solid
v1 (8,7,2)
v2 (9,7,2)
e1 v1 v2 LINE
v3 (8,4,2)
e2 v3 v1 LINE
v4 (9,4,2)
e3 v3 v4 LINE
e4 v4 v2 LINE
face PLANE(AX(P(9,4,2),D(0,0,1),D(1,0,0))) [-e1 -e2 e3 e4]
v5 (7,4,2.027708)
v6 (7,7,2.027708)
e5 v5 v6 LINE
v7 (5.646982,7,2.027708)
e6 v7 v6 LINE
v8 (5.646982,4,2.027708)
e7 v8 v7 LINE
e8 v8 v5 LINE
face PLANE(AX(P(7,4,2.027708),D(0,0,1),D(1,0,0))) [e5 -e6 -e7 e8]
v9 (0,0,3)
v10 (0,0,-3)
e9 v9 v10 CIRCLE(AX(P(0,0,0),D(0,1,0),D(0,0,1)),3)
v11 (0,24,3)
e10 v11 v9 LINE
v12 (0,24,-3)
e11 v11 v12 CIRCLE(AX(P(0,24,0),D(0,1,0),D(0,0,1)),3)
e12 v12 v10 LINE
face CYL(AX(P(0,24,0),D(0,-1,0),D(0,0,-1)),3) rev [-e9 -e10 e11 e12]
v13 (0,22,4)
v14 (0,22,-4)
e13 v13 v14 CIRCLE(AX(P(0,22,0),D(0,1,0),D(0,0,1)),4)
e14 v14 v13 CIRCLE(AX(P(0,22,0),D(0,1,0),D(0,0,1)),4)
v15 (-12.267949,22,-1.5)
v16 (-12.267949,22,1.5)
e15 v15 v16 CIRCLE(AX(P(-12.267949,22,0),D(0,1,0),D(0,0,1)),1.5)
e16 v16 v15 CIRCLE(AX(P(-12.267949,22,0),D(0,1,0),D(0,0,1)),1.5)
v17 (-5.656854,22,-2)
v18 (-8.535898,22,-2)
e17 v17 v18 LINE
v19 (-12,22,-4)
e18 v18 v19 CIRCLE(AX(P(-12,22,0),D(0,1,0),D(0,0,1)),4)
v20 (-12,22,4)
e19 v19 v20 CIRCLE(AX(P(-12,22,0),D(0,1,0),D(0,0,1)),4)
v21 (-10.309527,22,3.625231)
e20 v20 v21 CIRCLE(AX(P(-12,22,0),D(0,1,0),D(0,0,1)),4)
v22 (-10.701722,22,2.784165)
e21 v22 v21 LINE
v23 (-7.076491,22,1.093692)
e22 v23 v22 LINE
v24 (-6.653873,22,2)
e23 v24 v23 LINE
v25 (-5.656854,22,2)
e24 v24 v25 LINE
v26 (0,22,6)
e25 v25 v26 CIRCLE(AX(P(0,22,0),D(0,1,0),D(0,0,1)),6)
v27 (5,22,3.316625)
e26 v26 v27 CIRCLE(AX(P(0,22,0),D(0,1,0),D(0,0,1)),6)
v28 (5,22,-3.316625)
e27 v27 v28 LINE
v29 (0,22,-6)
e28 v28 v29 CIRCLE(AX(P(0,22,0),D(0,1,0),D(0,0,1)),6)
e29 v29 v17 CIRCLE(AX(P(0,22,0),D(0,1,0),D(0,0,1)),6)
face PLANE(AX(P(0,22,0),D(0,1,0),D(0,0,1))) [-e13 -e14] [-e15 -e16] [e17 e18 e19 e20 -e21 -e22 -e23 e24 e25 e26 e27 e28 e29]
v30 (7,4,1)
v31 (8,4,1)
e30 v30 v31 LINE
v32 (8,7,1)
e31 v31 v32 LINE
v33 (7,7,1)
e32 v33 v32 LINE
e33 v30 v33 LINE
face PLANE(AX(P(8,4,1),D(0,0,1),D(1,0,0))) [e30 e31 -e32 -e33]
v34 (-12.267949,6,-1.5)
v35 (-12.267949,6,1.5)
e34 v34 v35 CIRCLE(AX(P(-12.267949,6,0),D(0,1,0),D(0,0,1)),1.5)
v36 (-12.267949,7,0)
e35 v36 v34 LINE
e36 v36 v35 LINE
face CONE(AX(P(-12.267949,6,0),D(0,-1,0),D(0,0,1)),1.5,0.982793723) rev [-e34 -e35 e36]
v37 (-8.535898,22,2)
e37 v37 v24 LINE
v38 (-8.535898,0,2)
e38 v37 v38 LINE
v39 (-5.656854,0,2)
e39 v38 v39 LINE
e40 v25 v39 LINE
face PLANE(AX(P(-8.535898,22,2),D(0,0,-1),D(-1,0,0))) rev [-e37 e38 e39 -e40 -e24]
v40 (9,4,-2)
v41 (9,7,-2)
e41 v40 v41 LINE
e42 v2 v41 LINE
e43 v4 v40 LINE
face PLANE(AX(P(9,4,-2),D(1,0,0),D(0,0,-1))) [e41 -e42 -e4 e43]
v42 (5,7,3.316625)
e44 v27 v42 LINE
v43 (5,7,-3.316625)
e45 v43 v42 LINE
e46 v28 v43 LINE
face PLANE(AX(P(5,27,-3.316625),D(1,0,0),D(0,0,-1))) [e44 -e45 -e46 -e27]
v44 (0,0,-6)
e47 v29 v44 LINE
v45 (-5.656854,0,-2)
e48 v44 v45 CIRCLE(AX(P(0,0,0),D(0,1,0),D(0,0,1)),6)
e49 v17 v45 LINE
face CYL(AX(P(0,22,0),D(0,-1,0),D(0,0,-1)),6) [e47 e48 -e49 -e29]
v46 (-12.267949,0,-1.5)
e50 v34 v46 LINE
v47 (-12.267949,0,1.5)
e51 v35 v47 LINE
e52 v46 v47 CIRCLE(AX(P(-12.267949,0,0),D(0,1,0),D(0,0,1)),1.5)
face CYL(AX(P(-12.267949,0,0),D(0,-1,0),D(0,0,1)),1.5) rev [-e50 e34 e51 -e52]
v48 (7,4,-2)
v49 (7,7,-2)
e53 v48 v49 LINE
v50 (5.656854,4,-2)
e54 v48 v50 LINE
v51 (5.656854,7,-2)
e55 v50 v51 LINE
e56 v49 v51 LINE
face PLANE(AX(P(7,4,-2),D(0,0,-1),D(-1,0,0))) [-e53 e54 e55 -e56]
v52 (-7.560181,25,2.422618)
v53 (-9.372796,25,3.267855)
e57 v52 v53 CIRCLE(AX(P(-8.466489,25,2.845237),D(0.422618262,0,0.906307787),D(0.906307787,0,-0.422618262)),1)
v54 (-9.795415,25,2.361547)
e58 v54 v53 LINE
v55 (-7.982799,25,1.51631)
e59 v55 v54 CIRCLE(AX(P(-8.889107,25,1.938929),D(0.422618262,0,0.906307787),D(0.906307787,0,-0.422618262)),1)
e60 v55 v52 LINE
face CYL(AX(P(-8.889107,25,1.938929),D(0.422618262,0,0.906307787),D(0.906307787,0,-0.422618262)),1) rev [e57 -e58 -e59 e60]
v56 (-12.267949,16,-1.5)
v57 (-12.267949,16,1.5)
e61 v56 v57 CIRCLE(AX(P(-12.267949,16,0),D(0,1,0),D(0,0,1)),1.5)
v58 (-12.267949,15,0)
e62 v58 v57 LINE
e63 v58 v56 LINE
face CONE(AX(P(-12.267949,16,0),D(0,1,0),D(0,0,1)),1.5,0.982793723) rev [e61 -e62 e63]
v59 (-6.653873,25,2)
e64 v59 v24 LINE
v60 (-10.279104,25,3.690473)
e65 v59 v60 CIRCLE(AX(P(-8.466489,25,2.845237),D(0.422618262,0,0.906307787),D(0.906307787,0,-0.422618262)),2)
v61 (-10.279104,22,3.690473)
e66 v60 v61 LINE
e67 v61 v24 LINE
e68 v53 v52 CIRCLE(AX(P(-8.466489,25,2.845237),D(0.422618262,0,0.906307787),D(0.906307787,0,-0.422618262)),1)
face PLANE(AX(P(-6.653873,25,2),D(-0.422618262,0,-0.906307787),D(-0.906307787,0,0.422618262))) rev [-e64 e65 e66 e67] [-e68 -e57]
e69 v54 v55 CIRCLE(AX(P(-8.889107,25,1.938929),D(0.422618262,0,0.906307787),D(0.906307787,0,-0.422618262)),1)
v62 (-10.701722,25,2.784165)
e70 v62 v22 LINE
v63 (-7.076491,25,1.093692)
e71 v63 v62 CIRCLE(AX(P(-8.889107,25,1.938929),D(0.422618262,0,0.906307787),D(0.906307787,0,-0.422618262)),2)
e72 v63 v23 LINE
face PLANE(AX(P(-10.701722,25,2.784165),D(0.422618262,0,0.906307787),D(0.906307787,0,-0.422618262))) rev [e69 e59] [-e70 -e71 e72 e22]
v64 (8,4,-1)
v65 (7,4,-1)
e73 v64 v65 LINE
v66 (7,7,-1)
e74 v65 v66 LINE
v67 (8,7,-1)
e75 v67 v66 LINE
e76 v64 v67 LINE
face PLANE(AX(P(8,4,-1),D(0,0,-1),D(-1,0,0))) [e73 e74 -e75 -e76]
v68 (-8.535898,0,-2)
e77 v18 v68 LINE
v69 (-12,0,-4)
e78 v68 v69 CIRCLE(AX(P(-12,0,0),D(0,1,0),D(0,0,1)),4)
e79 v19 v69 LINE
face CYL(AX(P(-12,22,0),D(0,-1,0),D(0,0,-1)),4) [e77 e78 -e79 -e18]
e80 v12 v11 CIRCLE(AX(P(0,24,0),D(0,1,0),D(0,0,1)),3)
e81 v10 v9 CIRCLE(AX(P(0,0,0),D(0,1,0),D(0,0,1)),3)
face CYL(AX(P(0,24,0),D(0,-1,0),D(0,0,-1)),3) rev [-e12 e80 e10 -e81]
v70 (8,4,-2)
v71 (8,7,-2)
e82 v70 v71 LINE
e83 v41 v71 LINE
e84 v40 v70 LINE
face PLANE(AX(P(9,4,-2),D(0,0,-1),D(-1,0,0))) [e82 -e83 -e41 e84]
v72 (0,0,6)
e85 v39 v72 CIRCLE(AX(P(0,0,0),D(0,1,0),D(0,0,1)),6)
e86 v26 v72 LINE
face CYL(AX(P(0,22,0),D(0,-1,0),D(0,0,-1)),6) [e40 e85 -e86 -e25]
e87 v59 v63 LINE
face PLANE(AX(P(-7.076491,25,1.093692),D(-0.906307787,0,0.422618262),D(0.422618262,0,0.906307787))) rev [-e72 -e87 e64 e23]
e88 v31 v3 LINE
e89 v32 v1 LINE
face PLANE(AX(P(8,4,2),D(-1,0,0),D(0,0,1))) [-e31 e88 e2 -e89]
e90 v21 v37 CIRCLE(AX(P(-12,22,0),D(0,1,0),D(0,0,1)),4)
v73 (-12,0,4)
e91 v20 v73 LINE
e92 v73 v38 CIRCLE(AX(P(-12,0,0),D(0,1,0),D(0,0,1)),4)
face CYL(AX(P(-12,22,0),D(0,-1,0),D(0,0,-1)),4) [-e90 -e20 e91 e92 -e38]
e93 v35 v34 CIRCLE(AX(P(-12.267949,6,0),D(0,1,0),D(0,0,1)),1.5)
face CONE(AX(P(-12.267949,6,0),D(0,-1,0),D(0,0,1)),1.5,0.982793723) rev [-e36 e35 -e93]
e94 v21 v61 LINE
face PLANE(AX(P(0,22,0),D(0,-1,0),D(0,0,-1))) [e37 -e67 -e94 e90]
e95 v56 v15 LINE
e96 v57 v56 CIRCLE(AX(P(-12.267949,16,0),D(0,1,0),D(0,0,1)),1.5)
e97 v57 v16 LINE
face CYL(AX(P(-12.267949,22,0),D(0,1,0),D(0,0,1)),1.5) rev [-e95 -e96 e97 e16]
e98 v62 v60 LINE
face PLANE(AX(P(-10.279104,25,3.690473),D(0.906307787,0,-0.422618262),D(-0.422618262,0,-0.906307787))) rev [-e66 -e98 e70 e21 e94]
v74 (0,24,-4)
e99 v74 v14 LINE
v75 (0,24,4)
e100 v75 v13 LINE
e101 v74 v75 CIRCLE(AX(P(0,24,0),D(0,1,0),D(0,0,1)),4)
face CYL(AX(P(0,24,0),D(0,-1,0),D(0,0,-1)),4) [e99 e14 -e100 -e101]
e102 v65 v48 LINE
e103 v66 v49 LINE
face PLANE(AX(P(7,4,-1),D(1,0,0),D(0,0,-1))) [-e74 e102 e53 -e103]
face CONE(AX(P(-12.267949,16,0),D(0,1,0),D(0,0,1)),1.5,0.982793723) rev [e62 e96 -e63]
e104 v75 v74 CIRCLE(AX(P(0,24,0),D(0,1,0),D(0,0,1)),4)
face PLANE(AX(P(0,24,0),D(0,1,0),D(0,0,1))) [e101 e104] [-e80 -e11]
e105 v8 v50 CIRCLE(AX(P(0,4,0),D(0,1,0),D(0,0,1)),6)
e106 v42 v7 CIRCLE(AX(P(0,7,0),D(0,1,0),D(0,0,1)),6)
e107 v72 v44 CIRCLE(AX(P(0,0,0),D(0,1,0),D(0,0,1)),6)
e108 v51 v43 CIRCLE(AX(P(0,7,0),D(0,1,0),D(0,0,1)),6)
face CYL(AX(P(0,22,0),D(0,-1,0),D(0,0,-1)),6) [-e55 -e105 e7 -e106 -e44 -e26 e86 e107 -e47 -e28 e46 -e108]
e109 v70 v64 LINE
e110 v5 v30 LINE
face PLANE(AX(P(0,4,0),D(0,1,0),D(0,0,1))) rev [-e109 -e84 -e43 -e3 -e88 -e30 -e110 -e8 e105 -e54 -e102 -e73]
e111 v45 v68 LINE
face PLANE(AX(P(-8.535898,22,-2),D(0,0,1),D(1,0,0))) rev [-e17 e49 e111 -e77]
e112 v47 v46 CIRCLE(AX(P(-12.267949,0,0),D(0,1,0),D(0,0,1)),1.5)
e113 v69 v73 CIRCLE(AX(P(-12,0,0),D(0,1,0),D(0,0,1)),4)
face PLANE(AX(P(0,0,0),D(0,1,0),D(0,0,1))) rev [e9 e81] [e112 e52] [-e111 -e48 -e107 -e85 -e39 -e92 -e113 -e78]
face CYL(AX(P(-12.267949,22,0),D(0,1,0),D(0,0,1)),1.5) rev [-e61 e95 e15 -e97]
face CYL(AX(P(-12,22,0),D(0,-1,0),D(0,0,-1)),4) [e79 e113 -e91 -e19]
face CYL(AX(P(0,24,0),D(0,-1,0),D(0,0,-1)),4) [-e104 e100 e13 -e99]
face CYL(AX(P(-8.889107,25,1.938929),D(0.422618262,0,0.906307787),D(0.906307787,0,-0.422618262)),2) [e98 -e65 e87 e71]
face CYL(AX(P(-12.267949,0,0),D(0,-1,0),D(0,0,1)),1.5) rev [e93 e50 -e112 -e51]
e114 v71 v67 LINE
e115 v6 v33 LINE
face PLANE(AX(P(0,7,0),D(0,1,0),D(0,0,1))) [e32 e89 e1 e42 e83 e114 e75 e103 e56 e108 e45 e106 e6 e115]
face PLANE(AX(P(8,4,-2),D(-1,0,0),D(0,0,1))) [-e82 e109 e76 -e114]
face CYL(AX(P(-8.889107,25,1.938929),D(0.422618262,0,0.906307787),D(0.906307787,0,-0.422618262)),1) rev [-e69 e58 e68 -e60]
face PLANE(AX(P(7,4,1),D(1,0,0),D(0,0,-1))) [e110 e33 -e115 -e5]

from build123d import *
from build123d.topology import SkipClean

# Parameters (mm, degrees)
TWIN_BARREL_BODY_DEPTH = 22
EYE_TAB_DEPTH          = 3
EYE_TAB_BOSS_DEPTH     = 1
EYE_HOLE_SKETCH_R      = 1
EYE_HOLE_2_DEPTH       = 1
COLLAR_RING_SKETCH_R   = 4
COLLAR_RING_SKETCH_R_2 = 3
COLLAR_RING_8_DEPTH    = 2
COLLAR_BORE_SKETCH_R   = 3
COLLAR_BORE_CUT_DEPTH  = 28.856776554
NOTCHED_START          = -3
NOTCHED_LUG_DEPTH      = 3
LUG_SLOT_CUT_DEPTH     = 27.305892876


with BuildPart() as part:
    # Twin Barrel Profile Sketch → Twin Barrel Body (new body)
    with BuildSketch(Plane(origin=(0, 0, 0), x_dir=(1, 0, 0), z_dir=(0, 1, 0))):
        with BuildLine():
            Line((-8.535898385, 2), (-5.656854249, 2))
            ThreePointArc((-5.656854249, 2), (6, 0), (-5.656854249, -2))
            Line((-5.656854249, -2), (-8.535898385, -2))
            ThreePointArc((-8.535898385, -2), (-16, 0), (-8.535898385, 2))
        make_face()
    extrude(amount=TWIN_BARREL_BODY_DEPTH)

    # Eye Tab Sketch → Eye Tab (add)
    with BuildSketch(Plane(origin=(0, 22, 0), x_dir=(1, 0, 0), z_dir=(0, 1, 0))):
        Polygon((-10.701722418, -2.78416526), (-8.889106844, -1.938928736), (-7.07649127, -1.093692213), (-6.653873008, -2), (-10.279104156, -3.690473047), align=None)
    extrude(amount=EYE_TAB_DEPTH)

    # Eye Tab Boss Sketch → Eye Tab Boss (add)
    with BuildSketch(Plane(origin=(-0.422378498, 0, -0.905793612), x_dir=(0.9063077870366508, 0, -0.4226182617406976), z_dir=(0.4226182617406976, 0, 0.9063077870366508))):
        with BuildLine():
            Line((-10.875693444, 25), (-6.875693444, 25))
            ThreePointArc((-6.875693444, 25), (-8.875693444, 27), (-10.875693444, 25))
        make_face()
    extrude(amount=-EYE_TAB_BOSS_DEPTH)

    # Eye Hole Sketch → Eye Hole Ø2 (cut)
    with BuildSketch(Plane(origin=(-0.422378498, 0, -0.905793612), x_dir=(0.9063077870366508, 0, -0.4226182617406976), z_dir=(0.4226182617406976, 0, 0.9063077870366508))):
        with Locations((-8.875693444, 25)):
            Circle(EYE_HOLE_SKETCH_R)
    extrude(amount=-EYE_HOLE_2_DEPTH, mode=Mode.SUBTRACT)

    # Barrel Bore Profile Sketch → Barrel Bore Cut (revolve, cut)
    with BuildSketch(Plane.XY, mode=Mode.PRIVATE) as barrel_bore_cut_sk:
        Polygon((-12.267949192, 22), (-12.267949192, 15), (-13.767949192, 16), (-13.767949192, 22), align=None)
    barrel_bore_cut = revolve(barrel_bore_cut_sk.sketch.rotate(Axis((-12.267949192, 22, 0), (0, -1, 0)), 270), axis=Axis((-12.267949192, 22, 0), (0, -1, 0)), mode=Mode.SUBTRACT)

    # Barrel Bore Mirror: Barrel Bore Cut across plane
    add(barrel_bore_cut.mirror(Plane.ZX.offset(11)), mode=Mode.SUBTRACT)

    # Collar Ring Sketch → Collar Ring Ø8 (add)
    with BuildSketch(Plane(origin=(0, 22, 0), x_dir=(1, 0, 0), z_dir=(0, 1, 0))):
        with Locations(Location((0, 0, 0), (0, 0, 270))):
            Circle(COLLAR_RING_SKETCH_R)
        with Locations(Location((0, 0, 0), (0, 0, 270))):
            Circle(COLLAR_RING_SKETCH_R_2, mode=Mode.SUBTRACT)
    extrude(amount=COLLAR_RING_8_DEPTH)

    # Collar Bore Sketch → Collar Bore Cut (cut, through all)
    with BuildSketch(Plane(origin=(0, 22, 0), x_dir=(1, 0, 0), z_dir=(0, 1, 0))):
        with Locations(Location((0, 0, 0), (0, 0, 270))):
            Circle(COLLAR_BORE_SKETCH_R)
    extrude(amount=-COLLAR_BORE_CUT_DEPTH, mode=Mode.SUBTRACT)

    # Notched Lug Sketch → Notched Lug (add)
    with SkipClean():  # the faces are left unmerged after this step: merging them gives an invalid solid
        with BuildSketch(Plane(origin=(0, 7, 0), x_dir=(1, 0, 0), z_dir=(0, 1, 0)).offset(NOTCHED_START)):
            with BuildLine():
                Line((5, 3.31662479), (5, -3.31662479))
                ThreePointArc((5, -3.31662479), (5.362357836, -2.691675768), (5.646981669, -2.027707579))
                Line((5.646981669, -2.027707579), (7, -2.027707579))
                Line((7, -2.027707579), (7, -1))
                Line((7, -1), (8, -1))
                Line((8, -1), (8, -2))
                Line((8, -2), (9, -2))
                Line((9, -2), (9, 2))
                Line((9, 2), (8, 2))
                Line((8, 2), (8, 1))
                Line((8, 1), (7, 1))
                Line((7, 1), (7, 2))
                Line((7, 2), (5.656854249, 2))
                ThreePointArc((5.656854249, 2), (5.368939451, 2.678523692), (5, 3.31662479))
            make_face()
        extrude(amount=NOTCHED_LUG_DEPTH)

    # Lug Slot Sketch → Lug Slot Cut (cut, through all)
    with SkipClean():  # the faces are left unmerged after this step: merging them gives an invalid solid
        with BuildSketch(Plane(origin=(0, 7, 0), x_dir=(1, 0, 0), z_dir=(0, 1, 0))):
            with BuildLine():
                Line((5, 3.31662479), (5, -3.31662479))
                ThreePointArc((5, -3.31662479), (5.362357836, -2.691675768), (5.646981669, -2.027707579))
                ThreePointArc((5.646981669, -2.027707579), (5.956511293, 0.721091683), (5, 3.31662479))
            make_face()
        extrude(amount=LUG_SLOT_CUT_DEPTH, mode=Mode.SUBTRACT)


solid = part.part
